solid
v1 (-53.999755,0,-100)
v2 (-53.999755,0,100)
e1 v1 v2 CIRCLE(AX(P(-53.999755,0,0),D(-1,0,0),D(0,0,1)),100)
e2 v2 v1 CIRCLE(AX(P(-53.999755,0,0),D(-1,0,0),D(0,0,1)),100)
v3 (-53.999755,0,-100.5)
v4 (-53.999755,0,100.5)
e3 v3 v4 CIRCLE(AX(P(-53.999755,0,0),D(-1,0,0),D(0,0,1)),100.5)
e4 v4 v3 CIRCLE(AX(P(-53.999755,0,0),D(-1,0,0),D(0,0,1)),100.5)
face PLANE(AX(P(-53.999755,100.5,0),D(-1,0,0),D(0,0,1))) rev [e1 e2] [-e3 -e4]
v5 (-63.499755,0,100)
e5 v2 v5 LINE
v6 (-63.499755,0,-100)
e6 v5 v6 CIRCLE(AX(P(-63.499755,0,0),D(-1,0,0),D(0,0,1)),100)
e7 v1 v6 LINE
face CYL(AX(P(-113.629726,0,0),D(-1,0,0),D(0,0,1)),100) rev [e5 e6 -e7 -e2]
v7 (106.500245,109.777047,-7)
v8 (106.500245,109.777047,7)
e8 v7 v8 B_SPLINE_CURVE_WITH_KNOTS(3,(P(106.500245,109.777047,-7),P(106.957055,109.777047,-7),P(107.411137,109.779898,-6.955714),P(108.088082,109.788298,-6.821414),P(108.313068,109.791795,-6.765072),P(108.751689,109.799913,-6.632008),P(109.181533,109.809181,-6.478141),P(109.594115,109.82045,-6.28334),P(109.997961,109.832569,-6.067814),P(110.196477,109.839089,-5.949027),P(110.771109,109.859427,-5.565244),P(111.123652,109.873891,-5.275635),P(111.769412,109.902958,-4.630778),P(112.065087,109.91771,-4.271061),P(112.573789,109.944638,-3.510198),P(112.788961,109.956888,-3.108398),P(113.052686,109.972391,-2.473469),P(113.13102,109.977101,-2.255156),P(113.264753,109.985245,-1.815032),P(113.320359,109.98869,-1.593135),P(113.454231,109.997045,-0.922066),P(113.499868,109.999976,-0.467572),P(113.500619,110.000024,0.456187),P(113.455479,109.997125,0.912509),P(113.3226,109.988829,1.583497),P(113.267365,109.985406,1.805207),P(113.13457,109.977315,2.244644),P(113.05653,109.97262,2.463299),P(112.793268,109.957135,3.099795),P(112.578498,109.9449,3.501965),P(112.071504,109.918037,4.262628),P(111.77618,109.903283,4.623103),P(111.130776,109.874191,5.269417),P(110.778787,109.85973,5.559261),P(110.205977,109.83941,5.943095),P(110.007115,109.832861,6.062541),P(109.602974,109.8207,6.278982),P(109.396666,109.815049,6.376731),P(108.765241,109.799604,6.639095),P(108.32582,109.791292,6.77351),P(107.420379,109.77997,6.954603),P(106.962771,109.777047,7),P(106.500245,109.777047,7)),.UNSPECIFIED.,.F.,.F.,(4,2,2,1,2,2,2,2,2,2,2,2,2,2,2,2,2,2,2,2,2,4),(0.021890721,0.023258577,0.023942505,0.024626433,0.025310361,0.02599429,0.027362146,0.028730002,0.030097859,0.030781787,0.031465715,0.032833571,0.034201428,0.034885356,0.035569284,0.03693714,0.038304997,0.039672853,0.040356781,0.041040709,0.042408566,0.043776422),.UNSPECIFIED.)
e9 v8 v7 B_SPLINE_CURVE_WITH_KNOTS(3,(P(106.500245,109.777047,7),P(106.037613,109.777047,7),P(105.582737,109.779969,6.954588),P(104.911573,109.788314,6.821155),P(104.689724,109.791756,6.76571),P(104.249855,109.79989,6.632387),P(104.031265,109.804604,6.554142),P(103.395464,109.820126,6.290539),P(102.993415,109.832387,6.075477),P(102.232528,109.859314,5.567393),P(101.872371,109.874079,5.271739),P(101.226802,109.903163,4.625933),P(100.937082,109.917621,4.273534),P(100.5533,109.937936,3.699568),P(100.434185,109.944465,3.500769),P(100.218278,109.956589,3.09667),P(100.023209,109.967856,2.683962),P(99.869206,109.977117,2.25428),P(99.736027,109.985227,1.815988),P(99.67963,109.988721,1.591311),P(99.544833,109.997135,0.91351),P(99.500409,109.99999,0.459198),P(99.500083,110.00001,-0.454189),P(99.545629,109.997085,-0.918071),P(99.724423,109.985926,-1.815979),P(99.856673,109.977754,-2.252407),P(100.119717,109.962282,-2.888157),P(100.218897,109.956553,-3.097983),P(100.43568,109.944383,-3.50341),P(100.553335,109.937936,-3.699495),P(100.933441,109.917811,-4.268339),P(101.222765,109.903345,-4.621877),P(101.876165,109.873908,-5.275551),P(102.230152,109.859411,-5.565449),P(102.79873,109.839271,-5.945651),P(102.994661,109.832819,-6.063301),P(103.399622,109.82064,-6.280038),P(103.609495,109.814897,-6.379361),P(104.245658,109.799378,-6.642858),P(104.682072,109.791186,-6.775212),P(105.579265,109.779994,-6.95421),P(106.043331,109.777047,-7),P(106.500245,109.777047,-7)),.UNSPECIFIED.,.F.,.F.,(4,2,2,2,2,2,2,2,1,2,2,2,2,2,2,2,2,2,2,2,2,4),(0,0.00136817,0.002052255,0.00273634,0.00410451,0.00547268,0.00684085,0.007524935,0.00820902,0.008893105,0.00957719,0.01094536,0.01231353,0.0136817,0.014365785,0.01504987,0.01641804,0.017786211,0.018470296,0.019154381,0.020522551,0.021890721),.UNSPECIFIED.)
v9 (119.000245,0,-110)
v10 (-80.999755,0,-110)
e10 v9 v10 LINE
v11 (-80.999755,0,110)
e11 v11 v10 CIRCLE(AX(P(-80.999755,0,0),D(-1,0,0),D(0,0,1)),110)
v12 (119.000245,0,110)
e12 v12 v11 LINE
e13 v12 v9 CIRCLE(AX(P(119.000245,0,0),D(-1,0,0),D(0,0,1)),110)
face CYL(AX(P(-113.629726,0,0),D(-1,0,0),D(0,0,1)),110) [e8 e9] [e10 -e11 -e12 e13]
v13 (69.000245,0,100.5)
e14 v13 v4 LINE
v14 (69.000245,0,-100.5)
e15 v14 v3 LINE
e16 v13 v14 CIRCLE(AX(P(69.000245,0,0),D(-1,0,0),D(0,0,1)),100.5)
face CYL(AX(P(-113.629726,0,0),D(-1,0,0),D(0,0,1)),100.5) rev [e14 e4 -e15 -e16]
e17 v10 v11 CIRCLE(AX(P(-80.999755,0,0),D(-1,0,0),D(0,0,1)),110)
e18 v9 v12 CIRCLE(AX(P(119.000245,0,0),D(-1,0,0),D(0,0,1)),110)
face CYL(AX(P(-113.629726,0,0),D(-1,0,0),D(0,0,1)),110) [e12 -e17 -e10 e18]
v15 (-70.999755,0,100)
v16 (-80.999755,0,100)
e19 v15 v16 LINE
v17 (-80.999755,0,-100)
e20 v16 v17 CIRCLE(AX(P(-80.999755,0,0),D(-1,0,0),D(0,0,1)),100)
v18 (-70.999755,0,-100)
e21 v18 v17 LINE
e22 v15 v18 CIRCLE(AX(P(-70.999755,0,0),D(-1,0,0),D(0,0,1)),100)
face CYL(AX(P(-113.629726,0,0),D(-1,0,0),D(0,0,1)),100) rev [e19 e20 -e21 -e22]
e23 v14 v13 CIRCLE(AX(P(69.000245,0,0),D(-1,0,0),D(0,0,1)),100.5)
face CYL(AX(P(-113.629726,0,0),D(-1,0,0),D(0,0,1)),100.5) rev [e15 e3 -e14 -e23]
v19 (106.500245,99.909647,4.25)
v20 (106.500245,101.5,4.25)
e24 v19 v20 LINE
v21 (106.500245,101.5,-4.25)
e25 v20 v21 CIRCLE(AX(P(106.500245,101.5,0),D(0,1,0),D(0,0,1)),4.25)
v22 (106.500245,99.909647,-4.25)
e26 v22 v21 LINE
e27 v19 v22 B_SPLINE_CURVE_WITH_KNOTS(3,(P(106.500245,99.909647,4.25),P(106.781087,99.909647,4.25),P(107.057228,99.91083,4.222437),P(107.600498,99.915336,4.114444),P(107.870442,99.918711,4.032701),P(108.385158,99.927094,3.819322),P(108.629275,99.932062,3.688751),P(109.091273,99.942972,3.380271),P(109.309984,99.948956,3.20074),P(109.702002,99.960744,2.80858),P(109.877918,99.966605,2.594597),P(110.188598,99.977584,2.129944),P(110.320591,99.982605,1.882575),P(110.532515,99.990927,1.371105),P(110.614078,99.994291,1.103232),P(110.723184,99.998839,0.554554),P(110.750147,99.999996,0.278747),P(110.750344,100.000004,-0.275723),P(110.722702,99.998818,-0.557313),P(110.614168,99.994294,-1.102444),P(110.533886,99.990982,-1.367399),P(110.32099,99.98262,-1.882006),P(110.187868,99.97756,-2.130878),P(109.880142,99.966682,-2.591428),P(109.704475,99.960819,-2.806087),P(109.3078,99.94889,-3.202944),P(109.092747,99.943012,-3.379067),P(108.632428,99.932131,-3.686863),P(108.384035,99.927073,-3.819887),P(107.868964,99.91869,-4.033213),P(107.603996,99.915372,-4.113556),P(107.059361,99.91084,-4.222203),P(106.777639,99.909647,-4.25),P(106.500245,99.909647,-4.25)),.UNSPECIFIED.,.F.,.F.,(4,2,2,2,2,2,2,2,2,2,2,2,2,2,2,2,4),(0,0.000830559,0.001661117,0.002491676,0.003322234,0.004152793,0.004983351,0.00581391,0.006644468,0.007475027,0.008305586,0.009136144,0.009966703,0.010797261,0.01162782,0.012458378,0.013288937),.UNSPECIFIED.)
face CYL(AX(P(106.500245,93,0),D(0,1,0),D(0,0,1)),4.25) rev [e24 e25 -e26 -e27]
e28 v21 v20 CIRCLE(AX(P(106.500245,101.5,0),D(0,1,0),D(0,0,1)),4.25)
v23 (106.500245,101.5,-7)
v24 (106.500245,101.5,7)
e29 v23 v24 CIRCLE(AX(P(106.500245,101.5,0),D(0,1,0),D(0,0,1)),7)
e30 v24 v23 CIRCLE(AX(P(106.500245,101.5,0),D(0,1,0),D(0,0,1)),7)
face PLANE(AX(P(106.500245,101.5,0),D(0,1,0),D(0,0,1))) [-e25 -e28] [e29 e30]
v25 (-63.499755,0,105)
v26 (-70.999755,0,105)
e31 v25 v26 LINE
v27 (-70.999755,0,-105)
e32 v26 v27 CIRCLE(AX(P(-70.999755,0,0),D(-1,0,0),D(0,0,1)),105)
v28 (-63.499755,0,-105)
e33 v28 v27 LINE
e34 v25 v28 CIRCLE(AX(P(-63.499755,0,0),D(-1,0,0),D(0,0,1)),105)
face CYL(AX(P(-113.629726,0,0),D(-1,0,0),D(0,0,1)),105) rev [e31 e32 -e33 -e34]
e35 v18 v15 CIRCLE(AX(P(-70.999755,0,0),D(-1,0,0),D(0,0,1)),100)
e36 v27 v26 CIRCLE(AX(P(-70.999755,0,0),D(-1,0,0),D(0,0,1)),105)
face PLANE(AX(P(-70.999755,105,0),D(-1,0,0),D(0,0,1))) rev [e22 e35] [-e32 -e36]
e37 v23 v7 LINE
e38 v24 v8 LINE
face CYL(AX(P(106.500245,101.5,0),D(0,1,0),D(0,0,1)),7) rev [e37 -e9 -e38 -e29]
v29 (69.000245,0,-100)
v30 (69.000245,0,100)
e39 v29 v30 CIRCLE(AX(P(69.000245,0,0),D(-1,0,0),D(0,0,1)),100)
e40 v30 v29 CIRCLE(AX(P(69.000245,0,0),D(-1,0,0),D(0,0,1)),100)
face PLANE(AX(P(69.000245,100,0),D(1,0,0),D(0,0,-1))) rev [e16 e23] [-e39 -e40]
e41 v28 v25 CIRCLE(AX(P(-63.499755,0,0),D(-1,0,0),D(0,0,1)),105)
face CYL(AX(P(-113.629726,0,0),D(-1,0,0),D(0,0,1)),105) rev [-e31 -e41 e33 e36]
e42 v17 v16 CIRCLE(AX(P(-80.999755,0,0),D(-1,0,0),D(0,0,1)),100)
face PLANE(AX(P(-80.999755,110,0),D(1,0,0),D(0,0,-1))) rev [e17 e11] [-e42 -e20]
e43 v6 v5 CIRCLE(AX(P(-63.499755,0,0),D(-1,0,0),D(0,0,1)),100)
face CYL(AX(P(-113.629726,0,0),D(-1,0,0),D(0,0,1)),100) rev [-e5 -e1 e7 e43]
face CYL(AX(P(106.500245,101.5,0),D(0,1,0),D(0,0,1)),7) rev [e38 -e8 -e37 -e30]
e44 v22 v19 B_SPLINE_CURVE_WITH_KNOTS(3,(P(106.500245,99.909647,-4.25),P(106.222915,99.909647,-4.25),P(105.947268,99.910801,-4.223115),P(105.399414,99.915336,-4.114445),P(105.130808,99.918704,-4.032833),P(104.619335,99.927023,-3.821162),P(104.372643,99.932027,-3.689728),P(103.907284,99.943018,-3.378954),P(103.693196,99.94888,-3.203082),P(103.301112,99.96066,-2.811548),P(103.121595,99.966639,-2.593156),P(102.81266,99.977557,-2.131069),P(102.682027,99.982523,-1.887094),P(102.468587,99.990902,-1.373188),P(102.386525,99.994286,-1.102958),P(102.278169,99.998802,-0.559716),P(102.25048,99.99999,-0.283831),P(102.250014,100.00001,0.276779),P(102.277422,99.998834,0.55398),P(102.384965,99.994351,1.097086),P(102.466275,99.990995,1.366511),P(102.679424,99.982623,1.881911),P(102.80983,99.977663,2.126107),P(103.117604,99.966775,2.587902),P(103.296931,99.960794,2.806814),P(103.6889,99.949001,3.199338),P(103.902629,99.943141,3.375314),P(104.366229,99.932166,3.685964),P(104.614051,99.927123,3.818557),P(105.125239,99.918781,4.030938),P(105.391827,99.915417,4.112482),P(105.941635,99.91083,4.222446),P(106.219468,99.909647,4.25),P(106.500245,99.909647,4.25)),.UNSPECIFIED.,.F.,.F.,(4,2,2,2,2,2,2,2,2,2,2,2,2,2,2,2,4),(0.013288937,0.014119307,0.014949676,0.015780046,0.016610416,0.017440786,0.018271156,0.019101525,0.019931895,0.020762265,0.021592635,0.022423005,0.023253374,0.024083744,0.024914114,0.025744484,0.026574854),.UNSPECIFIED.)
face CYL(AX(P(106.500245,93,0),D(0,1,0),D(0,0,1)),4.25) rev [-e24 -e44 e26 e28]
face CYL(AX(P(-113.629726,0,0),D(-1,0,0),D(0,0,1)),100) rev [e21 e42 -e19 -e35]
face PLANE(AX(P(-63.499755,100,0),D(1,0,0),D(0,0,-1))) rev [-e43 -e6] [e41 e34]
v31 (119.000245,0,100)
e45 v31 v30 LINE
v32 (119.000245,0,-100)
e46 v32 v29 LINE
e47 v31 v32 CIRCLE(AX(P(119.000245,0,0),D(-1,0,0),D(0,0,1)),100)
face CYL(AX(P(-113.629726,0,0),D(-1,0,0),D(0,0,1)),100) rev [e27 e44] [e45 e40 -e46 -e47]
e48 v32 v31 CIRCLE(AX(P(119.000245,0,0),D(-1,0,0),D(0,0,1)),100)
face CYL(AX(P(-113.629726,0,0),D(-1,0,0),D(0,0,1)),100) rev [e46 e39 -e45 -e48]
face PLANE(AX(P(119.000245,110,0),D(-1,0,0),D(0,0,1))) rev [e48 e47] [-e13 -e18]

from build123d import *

# Parameters (mm, degrees)
SKETCH4_R          = 7
CUT_EXTRUDE1_DEPTH = 8.5
SKETCH5_R          = 4.25
CUT_EXTRUDE2_DEPTH = 8.5


with BuildPart() as part:
    # Sketch2 → Revolve1 (revolve)
    with BuildSketch(Plane.XY, mode=Mode.PRIVATE) as revolve1_sk:
        Polygon((-80.999754507, 110), (-80.999754507, 100), (-70.999754507, 100), (-70.999754507, 105), (-63.499754507, 105), (-63.499754507, 100), (-53.999754507, 100), (-53.999754507, 100.5), (69.000245493, 100.5), (69.000245493, 100), (119.000245493, 100), (119.000245493, 110), align=None)
    revolve(revolve1_sk.sketch.rotate(Axis((-113.629726069, 0, 0), (1, 0, 0)), 90), axis=Axis((-113.629726069, 0, 0), (1, 0, 0)))

    # Sketch4 → Cut-Extrude1 (cut)
    with BuildSketch(Plane(origin=(0, 110, 0), x_dir=(1, 0, 0), z_dir=(0, 1, 0))):
        with Locations(Location((106.500245493, 0, 0), (0, 0, 270))):
            Circle(SKETCH4_R)
    extrude(amount=-CUT_EXTRUDE1_DEPTH, mode=Mode.SUBTRACT)

    # Sketch5 → Cut-Extrude2 (cut)
    with BuildSketch(Plane(origin=(0, 101.5, 0), x_dir=(1, 0, 0), z_dir=(0, 1, 0))):
        with Locations(Location((106.500245493, 0, 0), (0, 0, 270))):
            Circle(SKETCH5_R)
    extrude(amount=-CUT_EXTRUDE2_DEPTH, mode=Mode.SUBTRACT)


solid = part.part
